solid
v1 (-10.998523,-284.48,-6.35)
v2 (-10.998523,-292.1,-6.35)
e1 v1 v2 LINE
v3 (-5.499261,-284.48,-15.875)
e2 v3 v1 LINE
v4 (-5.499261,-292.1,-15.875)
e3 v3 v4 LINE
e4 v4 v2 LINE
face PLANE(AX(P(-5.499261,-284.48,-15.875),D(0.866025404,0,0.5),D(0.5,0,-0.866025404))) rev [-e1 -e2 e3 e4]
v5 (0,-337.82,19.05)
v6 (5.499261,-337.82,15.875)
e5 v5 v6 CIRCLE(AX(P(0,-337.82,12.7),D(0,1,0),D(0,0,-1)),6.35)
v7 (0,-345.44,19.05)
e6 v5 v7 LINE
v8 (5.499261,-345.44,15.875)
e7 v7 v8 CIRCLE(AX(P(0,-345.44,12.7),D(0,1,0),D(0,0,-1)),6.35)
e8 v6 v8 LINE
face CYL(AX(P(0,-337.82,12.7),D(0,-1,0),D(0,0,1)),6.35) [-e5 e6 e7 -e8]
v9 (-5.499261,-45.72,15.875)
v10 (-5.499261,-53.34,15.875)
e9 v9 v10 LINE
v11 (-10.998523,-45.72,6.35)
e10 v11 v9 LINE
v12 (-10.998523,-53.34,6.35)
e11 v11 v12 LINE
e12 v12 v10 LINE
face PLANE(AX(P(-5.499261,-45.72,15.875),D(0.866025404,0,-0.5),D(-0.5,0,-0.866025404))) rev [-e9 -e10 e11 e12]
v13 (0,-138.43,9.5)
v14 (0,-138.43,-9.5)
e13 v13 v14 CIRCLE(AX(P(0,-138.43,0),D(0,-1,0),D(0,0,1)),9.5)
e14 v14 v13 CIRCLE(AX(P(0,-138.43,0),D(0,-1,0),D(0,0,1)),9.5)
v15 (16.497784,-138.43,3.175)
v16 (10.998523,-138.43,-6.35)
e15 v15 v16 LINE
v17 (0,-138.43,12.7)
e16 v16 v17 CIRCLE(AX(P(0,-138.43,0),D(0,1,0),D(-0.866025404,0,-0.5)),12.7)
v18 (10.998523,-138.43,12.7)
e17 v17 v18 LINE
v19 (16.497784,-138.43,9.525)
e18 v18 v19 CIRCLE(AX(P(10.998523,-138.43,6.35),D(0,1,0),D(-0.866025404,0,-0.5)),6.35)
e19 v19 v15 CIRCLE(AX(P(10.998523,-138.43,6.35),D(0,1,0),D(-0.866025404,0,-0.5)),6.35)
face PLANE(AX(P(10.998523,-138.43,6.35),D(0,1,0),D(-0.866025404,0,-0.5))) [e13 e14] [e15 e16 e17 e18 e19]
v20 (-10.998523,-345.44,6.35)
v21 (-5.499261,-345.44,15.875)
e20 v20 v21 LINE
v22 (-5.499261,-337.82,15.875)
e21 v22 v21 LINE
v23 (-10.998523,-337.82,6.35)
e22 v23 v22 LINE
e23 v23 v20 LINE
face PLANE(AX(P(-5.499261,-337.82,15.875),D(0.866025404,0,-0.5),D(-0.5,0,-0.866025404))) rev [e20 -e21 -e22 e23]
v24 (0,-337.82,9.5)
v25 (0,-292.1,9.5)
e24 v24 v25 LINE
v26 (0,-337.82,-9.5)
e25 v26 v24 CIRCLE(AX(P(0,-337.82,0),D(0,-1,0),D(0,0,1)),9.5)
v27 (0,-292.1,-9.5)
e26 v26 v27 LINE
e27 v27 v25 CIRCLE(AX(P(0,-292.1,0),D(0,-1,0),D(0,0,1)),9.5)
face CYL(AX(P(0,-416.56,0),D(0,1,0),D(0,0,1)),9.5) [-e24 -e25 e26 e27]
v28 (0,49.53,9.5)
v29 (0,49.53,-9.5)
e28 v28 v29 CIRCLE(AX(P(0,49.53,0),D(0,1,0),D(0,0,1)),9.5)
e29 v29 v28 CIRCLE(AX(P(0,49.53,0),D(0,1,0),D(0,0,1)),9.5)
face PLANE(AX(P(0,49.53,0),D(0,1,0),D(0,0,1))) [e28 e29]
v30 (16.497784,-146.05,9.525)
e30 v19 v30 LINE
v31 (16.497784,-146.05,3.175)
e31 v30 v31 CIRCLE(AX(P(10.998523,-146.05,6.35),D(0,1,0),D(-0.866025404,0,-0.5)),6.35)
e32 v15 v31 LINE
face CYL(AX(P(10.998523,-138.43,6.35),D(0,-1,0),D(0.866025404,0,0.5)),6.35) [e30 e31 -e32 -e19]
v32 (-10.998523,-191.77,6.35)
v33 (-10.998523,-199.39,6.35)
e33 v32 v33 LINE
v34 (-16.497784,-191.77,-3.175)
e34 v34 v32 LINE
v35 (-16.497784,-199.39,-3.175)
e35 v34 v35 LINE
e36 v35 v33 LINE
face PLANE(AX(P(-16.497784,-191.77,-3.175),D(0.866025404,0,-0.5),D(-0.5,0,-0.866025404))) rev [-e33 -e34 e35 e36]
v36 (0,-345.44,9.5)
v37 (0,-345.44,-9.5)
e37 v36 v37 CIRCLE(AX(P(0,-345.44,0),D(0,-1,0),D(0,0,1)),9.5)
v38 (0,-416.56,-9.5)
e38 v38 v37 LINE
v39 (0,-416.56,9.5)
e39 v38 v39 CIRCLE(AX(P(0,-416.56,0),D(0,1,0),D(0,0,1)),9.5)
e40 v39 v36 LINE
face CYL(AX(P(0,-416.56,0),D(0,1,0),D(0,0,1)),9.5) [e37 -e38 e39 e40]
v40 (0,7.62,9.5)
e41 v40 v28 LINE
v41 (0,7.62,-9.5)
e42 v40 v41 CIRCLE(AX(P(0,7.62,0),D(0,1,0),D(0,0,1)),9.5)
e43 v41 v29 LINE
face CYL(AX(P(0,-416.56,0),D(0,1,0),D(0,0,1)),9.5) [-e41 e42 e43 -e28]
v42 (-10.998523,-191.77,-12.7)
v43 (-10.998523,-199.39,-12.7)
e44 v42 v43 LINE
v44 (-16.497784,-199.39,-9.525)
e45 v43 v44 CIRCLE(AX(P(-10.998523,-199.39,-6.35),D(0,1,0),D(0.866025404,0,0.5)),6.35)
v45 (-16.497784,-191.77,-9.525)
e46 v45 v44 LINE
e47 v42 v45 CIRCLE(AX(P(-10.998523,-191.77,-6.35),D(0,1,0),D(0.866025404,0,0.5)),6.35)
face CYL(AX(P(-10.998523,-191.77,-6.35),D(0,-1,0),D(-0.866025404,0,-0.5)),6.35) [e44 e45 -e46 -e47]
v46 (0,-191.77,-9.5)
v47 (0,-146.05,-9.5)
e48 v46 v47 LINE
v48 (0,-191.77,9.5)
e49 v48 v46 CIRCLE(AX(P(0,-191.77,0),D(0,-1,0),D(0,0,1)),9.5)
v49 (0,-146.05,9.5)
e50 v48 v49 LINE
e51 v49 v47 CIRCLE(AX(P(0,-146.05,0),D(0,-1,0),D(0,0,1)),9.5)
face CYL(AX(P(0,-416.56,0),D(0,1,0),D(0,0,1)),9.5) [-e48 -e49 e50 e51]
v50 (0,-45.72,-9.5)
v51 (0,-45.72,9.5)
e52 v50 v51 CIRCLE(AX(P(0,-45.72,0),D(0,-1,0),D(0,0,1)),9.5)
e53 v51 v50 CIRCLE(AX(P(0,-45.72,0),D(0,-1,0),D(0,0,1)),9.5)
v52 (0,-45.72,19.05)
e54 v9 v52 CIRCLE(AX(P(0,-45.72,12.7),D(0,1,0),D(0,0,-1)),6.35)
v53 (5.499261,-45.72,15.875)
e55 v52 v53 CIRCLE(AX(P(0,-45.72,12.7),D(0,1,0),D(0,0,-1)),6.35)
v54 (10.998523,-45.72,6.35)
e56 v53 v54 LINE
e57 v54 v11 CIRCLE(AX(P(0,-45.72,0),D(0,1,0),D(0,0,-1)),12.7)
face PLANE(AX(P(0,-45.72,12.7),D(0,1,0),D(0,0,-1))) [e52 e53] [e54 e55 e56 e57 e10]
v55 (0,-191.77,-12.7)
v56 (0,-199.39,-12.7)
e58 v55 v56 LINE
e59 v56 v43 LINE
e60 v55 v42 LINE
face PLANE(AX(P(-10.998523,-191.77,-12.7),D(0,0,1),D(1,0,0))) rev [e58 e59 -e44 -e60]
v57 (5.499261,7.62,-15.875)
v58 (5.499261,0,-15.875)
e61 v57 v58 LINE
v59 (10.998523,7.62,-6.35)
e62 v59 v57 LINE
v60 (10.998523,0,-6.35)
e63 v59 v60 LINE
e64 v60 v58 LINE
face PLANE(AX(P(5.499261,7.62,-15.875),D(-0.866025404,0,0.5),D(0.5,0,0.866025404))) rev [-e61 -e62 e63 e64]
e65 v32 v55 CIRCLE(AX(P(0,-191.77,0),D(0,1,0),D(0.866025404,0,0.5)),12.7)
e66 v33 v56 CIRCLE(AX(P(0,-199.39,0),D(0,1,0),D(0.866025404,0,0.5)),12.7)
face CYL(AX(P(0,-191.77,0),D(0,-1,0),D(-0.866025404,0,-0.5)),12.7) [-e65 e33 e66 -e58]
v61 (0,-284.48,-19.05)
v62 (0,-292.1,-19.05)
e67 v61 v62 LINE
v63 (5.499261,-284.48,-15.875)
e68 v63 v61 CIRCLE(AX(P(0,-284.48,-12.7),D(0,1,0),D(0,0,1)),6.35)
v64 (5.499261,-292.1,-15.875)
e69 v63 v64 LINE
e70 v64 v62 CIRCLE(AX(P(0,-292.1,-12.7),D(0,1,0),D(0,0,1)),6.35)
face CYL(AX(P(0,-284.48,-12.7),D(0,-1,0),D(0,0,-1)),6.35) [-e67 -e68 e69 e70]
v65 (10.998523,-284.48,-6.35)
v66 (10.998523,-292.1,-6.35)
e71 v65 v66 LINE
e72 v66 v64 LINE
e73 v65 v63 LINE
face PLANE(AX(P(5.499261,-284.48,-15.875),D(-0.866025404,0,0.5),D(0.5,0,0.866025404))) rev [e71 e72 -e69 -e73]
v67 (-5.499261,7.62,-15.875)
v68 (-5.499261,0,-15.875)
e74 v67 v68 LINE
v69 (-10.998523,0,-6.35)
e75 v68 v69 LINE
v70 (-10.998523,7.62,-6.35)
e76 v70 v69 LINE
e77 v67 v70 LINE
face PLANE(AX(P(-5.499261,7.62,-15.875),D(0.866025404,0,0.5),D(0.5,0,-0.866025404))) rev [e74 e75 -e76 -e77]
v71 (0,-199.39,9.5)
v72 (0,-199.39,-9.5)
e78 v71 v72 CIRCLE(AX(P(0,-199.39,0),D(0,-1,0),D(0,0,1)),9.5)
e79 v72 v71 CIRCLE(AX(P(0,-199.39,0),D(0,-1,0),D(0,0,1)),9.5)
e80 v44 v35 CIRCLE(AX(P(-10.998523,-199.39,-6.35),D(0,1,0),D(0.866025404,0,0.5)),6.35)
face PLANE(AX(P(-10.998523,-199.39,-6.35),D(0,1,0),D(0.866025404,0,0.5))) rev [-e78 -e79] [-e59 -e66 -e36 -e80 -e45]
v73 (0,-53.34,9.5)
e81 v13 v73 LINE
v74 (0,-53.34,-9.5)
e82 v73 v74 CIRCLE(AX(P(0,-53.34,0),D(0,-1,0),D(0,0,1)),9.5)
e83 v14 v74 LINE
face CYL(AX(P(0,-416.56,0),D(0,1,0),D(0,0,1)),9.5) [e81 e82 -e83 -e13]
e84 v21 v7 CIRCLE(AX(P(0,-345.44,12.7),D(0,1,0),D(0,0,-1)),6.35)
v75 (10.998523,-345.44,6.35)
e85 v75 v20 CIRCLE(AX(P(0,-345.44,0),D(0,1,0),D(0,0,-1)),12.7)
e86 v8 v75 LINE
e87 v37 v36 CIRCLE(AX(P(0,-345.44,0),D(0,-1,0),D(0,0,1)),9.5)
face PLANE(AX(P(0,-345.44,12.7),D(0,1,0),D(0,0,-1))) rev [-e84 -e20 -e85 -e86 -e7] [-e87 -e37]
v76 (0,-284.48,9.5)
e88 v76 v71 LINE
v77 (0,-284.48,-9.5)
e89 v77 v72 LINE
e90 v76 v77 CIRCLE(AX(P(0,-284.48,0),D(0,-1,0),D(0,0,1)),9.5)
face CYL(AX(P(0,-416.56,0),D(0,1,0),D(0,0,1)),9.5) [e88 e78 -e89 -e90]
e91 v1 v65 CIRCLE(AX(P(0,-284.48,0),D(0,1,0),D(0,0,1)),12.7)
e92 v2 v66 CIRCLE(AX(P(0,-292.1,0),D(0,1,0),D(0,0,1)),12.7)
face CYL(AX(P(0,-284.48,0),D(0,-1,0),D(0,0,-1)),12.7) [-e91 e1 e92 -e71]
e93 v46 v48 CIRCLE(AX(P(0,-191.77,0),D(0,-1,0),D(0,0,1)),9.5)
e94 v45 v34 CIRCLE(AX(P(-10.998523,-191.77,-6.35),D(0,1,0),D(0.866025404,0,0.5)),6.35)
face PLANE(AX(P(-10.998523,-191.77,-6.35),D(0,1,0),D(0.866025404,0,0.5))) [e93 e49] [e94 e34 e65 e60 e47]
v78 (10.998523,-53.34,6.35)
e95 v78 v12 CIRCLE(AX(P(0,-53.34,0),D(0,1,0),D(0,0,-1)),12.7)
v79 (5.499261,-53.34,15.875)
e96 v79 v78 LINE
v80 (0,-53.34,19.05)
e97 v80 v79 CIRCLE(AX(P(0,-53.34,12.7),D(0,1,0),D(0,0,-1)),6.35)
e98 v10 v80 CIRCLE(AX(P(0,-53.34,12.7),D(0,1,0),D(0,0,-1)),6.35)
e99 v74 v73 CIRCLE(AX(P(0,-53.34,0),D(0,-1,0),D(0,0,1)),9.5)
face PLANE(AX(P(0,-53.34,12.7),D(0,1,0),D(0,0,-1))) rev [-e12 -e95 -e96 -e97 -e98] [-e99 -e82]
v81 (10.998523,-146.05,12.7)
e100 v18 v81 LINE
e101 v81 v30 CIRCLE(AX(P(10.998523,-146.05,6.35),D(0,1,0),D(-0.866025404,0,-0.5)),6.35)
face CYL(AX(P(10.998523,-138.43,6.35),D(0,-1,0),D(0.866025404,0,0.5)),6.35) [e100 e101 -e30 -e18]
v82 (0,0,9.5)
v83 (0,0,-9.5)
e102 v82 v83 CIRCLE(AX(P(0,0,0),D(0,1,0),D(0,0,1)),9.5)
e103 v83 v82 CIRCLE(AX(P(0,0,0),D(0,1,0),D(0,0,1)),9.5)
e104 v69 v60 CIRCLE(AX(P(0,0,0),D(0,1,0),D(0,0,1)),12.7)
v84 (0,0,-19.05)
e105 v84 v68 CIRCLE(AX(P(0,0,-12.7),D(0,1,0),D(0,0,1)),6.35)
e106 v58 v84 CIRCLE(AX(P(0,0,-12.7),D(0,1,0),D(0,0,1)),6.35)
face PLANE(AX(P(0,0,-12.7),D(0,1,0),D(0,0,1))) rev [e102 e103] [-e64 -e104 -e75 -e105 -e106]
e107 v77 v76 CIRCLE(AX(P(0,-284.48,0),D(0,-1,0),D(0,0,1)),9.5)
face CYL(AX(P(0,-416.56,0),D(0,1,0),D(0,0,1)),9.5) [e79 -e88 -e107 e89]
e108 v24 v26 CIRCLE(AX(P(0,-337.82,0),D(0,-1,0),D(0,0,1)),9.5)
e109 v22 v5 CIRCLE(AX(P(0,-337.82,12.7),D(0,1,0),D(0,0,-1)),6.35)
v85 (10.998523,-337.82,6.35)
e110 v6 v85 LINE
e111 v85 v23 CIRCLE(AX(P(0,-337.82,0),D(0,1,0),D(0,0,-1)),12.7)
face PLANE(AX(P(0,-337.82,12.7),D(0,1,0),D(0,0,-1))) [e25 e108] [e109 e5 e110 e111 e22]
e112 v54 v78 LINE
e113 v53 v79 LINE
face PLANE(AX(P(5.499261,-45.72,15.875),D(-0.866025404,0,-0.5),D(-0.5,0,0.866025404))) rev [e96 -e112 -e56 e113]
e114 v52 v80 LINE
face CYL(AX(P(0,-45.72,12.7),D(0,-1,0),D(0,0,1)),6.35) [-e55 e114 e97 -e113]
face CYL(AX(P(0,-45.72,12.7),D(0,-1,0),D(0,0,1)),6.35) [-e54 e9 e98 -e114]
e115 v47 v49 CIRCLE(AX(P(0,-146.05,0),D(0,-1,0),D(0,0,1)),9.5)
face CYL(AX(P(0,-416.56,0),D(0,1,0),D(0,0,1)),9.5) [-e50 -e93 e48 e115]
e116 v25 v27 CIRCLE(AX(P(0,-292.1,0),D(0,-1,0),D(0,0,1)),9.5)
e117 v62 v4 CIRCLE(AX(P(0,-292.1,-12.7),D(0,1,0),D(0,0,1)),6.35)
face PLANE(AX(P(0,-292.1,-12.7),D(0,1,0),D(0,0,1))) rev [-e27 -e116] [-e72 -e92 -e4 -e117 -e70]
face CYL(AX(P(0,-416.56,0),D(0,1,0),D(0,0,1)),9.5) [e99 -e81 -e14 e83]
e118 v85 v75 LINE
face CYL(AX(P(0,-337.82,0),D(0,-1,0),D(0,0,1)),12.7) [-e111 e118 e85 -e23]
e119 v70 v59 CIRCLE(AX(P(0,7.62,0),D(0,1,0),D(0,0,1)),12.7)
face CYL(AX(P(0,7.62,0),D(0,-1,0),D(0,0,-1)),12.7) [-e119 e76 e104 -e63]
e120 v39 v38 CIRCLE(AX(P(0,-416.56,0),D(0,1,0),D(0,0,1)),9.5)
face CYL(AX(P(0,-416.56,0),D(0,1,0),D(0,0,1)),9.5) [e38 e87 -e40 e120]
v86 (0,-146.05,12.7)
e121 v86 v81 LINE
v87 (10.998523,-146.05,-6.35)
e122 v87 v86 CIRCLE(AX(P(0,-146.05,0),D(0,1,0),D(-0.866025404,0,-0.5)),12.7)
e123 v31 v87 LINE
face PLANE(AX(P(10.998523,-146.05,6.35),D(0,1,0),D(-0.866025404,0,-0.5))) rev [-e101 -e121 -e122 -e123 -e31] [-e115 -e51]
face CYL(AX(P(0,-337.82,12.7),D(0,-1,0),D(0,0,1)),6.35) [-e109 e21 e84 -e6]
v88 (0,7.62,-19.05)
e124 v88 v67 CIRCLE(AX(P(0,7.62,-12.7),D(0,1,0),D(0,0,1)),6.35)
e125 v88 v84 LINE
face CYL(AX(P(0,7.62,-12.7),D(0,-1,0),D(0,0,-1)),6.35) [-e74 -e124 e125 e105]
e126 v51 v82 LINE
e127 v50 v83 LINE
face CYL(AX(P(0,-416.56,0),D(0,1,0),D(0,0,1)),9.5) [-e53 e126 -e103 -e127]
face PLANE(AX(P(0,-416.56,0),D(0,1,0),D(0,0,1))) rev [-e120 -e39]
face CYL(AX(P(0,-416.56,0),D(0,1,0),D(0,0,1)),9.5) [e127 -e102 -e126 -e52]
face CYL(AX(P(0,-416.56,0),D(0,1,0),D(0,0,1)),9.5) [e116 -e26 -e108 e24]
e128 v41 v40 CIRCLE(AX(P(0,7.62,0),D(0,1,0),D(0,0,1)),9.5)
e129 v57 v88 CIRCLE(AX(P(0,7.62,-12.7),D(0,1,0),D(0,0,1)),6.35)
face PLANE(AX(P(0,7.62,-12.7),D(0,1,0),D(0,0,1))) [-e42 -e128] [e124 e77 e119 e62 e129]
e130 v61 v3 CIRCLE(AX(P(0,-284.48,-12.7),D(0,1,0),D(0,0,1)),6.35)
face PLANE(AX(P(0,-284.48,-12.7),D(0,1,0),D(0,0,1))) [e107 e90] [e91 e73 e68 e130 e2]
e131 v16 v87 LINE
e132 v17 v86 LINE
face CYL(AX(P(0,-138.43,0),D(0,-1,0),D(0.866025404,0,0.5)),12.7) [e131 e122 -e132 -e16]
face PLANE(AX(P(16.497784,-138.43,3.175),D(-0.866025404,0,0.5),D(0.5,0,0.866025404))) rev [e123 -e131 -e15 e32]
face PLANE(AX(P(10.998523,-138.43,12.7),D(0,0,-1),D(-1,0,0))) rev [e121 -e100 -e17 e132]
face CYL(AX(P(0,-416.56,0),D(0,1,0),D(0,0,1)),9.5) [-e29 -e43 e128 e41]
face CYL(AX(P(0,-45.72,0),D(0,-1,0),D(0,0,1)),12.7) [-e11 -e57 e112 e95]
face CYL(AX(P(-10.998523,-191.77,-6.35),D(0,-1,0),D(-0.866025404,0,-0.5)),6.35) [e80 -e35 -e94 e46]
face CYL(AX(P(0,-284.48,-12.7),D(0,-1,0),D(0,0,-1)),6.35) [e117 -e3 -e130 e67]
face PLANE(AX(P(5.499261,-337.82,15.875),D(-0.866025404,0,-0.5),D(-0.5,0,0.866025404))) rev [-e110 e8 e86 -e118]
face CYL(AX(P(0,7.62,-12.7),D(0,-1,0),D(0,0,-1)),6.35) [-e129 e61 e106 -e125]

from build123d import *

# Parameters (mm, degrees)
CAM_LOBE_DEPTH                 = 7.62
CAM_LOBE_PAIR_PATTERN_2X_COUNT = 2
CAM_LOBE_PAIR_PATTERN_2X_PITCH = 53.34
ROTATE_LOBE_180DEG_ANGLE       = 180
LOBE_SET_PATTERN_3X_COUNT      = 3
LOBE_SET_PATTERN_3X_PITCH      = 146.05
ROTATE_LOBE_SET_120DEG_ANGLE   = 120
CAMSHAFT_START                 = 49.53
SHAFT_PROFILE_SKETCH_R         = 9.5
CAMSHAFT_SHAFT_DEPTH           = 466.09


with BuildPart() as part:
    # Cam Lobe Profile Sketch → Cam Lobe (new body)
    with BuildSketch(Plane(origin=(0, 0, 0), x_dir=(1, 0, 0), z_dir=(0, 1, 0))):
        with BuildLine():
            Line((-5.499261314, 15.875), (-10.998522628, 6.35))
            ThreePointArc((-10.998522628, 6.35), (0, -12.7), (10.998522628, 6.35))
            Line((10.998522628, 6.35), (5.499261314, 15.875))
            ThreePointArc((5.499261314, 15.875), (0, 19.05), (-5.499261314, 15.875))
        make_face()
    extrude(amount=CAM_LOBE_DEPTH)


with BuildPart() as cam_lobe_pair_pattern_2x_1:
    # Cam Lobe Pair Pattern 2x: pattern copy
    add(part.part.moved(Location(Vector(0, -1, 0) * (1 * CAM_LOBE_PAIR_PATTERN_2X_PITCH))))


with BuildPart() as cam_lobe_pair_pattern_2x_1_1:
    # Rotate Lobe 180deg: moved
    add(cam_lobe_pair_pattern_2x_1.part.rotate(Axis((0, 0, 0), (0, 1, 0)), ROTATE_LOBE_180DEG_ANGLE))


with BuildPart() as lobe_set_pattern_3x_1:
    # Lobe Set Pattern 3x: pattern copy
    add(part.part.moved(Location(Vector(0, -1, 0) * (1 * LOBE_SET_PATTERN_3X_PITCH))))


with BuildPart() as lobe_set_pattern_3x_2:
    # Lobe Set Pattern 3x: pattern copy
    add(part.part.moved(Location(Vector(0, -1, 0) * (2 * LOBE_SET_PATTERN_3X_PITCH))))


with BuildPart() as lobe_set_pattern_3x_3:
    # Lobe Set Pattern 3x: pattern copy
    add(cam_lobe_pair_pattern_2x_1_1.part.moved(Location(Vector(0, -1, 0) * (1 * LOBE_SET_PATTERN_3X_PITCH))))


with BuildPart() as lobe_set_pattern_3x_4:
    # Lobe Set Pattern 3x: pattern copy
    add(cam_lobe_pair_pattern_2x_1_1.part.moved(Location(Vector(0, -1, 0) * (2 * LOBE_SET_PATTERN_3X_PITCH))))


with BuildPart() as lobe_set_pattern_3x_1_1:
    # Rotate Lobe Set 120deg: moved
    add(lobe_set_pattern_3x_1.part.rotate(Axis((0, 0, 0), (0, -1, 0)), ROTATE_LOBE_SET_120DEG_ANGLE))


with BuildPart() as lobe_set_pattern_3x_3_1:
    # Rotate Lobe Set 120deg: moved
    add(lobe_set_pattern_3x_3.part.rotate(Axis((0, 0, 0), (0, -1, 0)), ROTATE_LOBE_SET_120DEG_ANGLE))


with BuildPart() as part_1:
    add(part.part)

    add(cam_lobe_pair_pattern_2x_1_1.part)  # Camshaft Shaft merges Cam Lobe Pair Pattern 2x_1

    add(lobe_set_pattern_3x_1_1.part)  # Camshaft Shaft merges Lobe Set Pattern 3x_1

    add(lobe_set_pattern_3x_2.part)  # Camshaft Shaft merges Lobe Set Pattern 3x_2

    add(lobe_set_pattern_3x_3_1.part)  # Camshaft Shaft merges Lobe Set Pattern 3x_3

    add(lobe_set_pattern_3x_4.part)  # Camshaft Shaft merges Lobe Set Pattern 3x_4
    # Shaft Profile Sketch → Camshaft Shaft (add)
    with BuildSketch(Plane(origin=(0, 0, 0), x_dir=(1, 0, 0), z_dir=(0, 1, 0)).offset(CAMSHAFT_START)):
        with Locations(Location((0, 0, 0), (0, 0, 270))):
            Circle(SHAFT_PROFILE_SKETCH_R)
    extrude(amount=-CAMSHAFT_SHAFT_DEPTH)


solid = part_1.part
